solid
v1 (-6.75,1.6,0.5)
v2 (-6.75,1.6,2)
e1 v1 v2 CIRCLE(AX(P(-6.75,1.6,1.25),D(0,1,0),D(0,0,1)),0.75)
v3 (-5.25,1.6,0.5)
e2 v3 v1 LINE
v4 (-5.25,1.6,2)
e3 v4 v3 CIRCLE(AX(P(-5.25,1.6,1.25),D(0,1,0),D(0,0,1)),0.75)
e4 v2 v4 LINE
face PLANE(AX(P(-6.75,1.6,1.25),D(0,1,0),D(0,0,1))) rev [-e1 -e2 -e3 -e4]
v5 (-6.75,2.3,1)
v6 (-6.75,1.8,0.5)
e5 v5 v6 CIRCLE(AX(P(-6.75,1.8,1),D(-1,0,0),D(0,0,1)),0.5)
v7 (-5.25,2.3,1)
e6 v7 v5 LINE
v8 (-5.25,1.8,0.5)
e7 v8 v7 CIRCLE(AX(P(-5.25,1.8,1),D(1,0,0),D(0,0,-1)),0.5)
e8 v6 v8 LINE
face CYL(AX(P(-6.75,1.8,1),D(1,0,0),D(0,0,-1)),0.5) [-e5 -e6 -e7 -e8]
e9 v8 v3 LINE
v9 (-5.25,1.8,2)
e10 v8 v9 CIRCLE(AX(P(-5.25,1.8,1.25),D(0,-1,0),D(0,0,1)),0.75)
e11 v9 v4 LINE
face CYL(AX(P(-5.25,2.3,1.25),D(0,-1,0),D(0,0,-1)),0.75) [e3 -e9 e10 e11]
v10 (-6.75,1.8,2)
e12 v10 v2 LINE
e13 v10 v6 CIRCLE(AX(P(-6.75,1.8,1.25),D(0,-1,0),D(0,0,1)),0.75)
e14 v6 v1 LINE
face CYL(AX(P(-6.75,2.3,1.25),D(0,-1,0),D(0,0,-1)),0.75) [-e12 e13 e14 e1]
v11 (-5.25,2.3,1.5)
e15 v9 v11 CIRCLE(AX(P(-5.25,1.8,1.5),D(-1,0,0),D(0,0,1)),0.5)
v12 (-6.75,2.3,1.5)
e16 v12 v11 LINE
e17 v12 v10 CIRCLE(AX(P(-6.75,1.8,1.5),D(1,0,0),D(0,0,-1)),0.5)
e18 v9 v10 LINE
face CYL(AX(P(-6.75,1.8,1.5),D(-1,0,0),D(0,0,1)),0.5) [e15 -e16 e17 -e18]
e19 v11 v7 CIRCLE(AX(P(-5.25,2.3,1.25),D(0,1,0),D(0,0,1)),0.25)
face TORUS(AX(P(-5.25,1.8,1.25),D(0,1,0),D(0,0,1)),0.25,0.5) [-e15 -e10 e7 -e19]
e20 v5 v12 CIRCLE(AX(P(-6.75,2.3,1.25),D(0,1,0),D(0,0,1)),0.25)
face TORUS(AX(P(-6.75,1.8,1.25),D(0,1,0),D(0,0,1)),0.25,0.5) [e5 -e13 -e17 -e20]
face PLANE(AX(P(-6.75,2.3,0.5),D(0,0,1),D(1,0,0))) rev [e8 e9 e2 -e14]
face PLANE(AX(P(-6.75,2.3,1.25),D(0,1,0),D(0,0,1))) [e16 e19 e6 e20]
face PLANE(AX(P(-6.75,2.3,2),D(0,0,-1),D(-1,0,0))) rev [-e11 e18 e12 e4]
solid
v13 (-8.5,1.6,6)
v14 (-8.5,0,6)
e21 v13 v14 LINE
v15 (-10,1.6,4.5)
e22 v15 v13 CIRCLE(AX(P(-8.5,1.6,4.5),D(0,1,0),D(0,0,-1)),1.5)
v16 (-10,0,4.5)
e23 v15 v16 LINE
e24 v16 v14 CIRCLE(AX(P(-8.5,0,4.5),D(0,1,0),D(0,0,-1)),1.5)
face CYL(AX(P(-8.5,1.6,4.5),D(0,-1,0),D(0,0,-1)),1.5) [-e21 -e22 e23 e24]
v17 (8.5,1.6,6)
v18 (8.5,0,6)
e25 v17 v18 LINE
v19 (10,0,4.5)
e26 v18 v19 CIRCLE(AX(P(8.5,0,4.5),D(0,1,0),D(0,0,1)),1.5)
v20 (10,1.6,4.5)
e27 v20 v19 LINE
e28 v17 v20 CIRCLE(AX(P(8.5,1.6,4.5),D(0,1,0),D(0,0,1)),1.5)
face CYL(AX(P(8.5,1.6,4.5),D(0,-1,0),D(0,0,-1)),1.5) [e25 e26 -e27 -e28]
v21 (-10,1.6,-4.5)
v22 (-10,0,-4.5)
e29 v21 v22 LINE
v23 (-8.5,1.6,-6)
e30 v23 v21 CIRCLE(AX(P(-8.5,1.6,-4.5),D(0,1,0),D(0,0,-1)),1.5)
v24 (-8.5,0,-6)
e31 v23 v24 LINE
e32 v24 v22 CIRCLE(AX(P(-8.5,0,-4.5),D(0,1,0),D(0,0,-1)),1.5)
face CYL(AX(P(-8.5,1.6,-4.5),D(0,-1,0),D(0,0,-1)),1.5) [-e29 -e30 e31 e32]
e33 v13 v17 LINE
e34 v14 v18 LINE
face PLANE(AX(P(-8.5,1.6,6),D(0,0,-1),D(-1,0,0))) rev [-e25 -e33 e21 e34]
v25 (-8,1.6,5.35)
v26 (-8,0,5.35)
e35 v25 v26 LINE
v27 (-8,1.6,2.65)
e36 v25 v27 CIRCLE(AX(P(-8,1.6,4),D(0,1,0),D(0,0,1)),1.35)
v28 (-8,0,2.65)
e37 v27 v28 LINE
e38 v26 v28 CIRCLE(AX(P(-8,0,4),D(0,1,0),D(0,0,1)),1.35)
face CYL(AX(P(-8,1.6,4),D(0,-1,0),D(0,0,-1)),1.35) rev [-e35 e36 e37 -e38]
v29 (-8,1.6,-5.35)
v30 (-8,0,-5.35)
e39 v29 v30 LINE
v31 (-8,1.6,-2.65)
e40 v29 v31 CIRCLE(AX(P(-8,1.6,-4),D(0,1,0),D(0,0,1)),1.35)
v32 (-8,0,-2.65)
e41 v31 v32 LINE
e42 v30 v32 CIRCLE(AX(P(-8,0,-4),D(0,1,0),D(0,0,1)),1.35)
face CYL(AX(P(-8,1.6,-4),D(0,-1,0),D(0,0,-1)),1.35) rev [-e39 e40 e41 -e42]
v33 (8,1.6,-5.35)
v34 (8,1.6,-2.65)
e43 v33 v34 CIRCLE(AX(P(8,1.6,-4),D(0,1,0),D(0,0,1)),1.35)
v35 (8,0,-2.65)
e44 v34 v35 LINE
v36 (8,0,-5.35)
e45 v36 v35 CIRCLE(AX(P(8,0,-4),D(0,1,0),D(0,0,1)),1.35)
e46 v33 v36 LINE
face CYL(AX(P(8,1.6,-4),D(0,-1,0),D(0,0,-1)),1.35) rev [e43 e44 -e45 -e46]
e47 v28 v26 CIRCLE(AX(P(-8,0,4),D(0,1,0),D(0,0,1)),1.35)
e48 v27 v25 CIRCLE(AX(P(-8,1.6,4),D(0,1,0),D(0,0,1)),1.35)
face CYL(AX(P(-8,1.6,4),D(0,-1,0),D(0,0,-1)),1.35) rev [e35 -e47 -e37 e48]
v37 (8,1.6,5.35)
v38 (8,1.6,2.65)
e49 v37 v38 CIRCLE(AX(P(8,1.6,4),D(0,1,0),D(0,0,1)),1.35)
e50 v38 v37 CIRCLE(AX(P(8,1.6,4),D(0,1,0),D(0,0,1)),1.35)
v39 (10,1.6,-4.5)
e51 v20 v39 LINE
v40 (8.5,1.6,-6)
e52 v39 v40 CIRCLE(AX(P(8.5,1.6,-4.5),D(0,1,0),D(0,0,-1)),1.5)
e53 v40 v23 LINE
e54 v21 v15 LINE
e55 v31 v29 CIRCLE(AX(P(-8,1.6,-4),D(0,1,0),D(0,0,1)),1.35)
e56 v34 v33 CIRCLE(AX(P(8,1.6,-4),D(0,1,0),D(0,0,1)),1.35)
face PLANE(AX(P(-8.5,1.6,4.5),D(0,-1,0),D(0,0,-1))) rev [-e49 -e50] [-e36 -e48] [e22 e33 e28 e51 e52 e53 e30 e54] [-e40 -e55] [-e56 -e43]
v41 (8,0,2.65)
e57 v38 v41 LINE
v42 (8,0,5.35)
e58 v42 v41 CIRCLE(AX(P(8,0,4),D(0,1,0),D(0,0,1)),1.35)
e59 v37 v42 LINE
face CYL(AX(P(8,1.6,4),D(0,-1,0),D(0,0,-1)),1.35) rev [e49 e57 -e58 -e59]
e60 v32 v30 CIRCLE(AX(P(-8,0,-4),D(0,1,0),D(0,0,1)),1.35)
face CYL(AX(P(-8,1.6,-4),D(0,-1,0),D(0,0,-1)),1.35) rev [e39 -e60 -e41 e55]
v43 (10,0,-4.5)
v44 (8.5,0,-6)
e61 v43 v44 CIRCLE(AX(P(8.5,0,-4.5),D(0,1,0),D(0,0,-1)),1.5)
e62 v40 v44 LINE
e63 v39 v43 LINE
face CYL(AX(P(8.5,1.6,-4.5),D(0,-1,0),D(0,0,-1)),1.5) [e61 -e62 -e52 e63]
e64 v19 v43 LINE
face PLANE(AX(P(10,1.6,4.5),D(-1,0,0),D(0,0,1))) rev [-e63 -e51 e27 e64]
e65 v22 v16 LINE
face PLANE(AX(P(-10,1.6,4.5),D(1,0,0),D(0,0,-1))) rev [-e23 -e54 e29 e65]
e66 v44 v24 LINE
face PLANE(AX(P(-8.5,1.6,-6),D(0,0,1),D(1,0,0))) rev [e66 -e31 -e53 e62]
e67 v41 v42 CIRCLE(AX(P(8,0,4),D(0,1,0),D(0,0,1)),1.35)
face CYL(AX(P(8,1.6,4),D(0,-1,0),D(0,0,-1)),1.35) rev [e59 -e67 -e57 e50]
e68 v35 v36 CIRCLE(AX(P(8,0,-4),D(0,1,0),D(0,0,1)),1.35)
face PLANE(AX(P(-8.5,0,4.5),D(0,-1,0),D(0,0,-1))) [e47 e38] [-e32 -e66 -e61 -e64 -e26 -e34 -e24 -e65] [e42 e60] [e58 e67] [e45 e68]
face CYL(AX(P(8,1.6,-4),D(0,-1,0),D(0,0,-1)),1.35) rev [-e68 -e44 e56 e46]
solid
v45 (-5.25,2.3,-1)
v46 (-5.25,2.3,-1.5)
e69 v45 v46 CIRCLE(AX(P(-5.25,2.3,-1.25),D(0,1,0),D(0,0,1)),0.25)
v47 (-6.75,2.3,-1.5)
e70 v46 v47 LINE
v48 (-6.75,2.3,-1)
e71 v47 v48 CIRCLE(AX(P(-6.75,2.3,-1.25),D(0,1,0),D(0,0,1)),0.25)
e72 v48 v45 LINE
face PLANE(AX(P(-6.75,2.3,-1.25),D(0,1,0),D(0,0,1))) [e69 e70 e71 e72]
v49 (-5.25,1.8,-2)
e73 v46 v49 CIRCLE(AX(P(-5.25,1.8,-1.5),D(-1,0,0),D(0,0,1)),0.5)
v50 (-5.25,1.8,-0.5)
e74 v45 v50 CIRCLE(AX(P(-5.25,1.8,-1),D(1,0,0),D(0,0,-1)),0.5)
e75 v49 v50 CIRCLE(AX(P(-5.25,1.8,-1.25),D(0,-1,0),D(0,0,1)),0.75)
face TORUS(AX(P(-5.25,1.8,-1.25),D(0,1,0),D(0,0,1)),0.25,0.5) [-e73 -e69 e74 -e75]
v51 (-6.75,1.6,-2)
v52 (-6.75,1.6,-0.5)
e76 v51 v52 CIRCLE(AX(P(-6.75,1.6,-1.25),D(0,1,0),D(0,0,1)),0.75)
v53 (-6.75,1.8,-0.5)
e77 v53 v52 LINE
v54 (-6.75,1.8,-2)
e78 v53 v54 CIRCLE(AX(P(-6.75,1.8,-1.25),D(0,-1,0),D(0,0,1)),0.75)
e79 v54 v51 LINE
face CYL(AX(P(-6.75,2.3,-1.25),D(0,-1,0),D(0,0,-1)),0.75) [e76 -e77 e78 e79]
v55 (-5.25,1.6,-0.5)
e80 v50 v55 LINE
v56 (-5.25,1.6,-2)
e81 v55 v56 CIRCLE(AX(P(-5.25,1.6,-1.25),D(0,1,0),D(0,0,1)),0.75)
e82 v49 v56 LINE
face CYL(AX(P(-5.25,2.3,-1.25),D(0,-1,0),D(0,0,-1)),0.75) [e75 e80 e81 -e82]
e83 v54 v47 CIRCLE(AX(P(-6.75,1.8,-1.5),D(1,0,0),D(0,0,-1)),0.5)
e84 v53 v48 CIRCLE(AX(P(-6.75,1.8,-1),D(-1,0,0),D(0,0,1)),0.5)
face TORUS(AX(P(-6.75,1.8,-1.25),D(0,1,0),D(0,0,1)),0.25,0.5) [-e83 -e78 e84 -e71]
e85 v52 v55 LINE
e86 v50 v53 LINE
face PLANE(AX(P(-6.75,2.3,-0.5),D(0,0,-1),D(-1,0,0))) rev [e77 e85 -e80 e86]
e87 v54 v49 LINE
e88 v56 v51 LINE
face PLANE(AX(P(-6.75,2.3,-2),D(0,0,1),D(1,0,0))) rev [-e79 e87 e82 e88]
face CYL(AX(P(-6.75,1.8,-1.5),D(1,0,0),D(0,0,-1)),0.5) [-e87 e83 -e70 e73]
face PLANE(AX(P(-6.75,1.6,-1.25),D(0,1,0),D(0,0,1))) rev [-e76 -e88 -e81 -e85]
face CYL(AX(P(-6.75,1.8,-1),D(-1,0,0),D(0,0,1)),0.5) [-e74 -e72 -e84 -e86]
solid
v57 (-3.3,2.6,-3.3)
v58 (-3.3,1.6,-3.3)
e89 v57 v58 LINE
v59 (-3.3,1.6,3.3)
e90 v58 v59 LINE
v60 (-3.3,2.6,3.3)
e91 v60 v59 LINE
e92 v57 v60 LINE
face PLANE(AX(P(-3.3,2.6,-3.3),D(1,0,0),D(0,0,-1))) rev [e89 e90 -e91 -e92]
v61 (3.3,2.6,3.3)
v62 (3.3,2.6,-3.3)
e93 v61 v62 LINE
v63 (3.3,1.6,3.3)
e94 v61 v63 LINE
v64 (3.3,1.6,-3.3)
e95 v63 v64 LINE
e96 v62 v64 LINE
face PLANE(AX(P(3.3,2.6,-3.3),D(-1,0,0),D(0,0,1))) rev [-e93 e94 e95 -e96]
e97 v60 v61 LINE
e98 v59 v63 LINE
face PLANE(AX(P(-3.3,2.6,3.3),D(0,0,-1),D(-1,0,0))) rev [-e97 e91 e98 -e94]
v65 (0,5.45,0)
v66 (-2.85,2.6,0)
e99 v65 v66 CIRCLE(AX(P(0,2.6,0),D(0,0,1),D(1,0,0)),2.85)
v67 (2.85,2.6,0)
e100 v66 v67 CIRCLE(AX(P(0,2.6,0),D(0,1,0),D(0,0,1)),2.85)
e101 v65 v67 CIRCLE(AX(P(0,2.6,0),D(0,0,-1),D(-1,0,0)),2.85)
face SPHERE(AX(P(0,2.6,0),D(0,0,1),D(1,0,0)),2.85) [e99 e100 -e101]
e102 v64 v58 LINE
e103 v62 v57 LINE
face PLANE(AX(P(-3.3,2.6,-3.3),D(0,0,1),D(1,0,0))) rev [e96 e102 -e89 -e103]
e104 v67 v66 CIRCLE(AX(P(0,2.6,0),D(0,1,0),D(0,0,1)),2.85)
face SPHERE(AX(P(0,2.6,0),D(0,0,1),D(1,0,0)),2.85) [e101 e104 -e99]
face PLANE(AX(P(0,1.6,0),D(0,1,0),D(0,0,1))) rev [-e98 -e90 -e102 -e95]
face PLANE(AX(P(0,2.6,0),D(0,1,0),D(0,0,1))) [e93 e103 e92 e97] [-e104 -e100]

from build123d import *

# Parameters (mm, degrees)
ALUMINIUM_BASE_PLATE_DEPTH        = 1.6
SKETCH7_R                         = 1.35
SCREW_HOLE_DEPTH                  = 12.771151176
SKETCH_587_W                      = 6.6
SKETCH_587_H                      = 6.6
LED_BEAD_BOARD_DEPTH              = 1
SOLDER_JOINT_BASE_OUTLINE_DEPTH   = 0.7
SOLDER_JOINT_BASE_OUTLINE_2_DEPTH = 0.7
SOLDER_JOINT_1_R                  = 0.5
SOLDER_JOINT_2_R                  = 0.5


with BuildPart() as part:
    # Aluminium base plate outline → Aluminium base plate (new body)
    with BuildSketch(Plane(origin=(0, 0, 0), x_dir=(1, 0, 0), z_dir=(0, 1, 0))):
        with BuildLine():
            Line((-8.5, -6), (8.5, -6))
            ThreePointArc((8.5, -6), (9.560660172, -5.560660172), (10, -4.5))
            Line((10, -4.5), (10, 4.5))
            ThreePointArc((10, 4.5), (9.560660172, 5.560660172), (8.5, 6))
            Line((8.5, 6), (-8.5, 6))
            ThreePointArc((-8.5, 6), (-9.560660172, 5.560660172), (-10, 4.5))
            Line((-10, 4.5), (-10, -4.5))
            ThreePointArc((-10, -4.5), (-9.560660172, -5.560660172), (-8.5, -6))
        make_face()
    extrude(amount=ALUMINIUM_BASE_PLATE_DEPTH)

    # Sketch7 → Screw hole (cut, through all)
    with BuildSketch(Plane(origin=(0, 0, 0), x_dir=(1, 0, 0), z_dir=(0, 1, 0))):
        with Locations(Location((-8, -4, 0), (0, 0, 270))):
            Circle(SKETCH7_R)
        with Locations(Location((8, -4, 0), (0, 0, 270))):
            Circle(SKETCH7_R)
        with Locations(Location((8, 4, 0), (0, 0, 270))):
            Circle(SKETCH7_R)
        with Locations(Location((-8, 4, 0), (0, 0, 270))):
            Circle(SKETCH7_R)
    extrude(amount=SCREW_HOLE_DEPTH, mode=Mode.SUBTRACT)


with BuildPart() as body_2:
    # Sketch 587 → LED bead board (new body)
    with BuildSketch(Plane(origin=(0, 1.6, 0), x_dir=(1, 0, 0), z_dir=(0, 1, 0))):
        Rectangle(SKETCH_587_W, SKETCH_587_H)
    extrude(amount=LED_BEAD_BOARD_DEPTH)

    # LED bead rotation base → LED bead (revolve)
    with BuildSketch(Plane.XY):
        with BuildLine():
            Line((0, 2.6), (2.85, 2.6))
            ThreePointArc((2.85, 2.6), (2.015254326, 4.615254326), (0, 5.45))
            Line((0, 5.45), (0, 2.6))
        make_face()
    revolve(axis=Axis((0, 2.6, 0), (0, 1, 0)))


with BuildPart() as body_3:
    # Solder pad → Solder joint base outline (new body)
    with BuildSketch(Plane(origin=(0, 1.6, 0), x_dir=(1, 0, 0), z_dir=(0, 1, 0))):
        with BuildLine():
            Line((-6.75, 2), (-5.25, 2))
            ThreePointArc((-5.25, 2), (-4.5, 1.25), (-5.25, 0.5))
            Line((-5.25, 0.5), (-6.75, 0.5))
            ThreePointArc((-6.75, 0.5), (-7.5, 1.25), (-6.75, 2))
        make_face()
    extrude(amount=SOLDER_JOINT_BASE_OUTLINE_DEPTH)

    # Solder joint 1
    solder_joint_1_edges = [body_3.edges().sort_by_distance(p)[0] for p in [
        (-4.5, 2.3, -1.25),
        (-6, 2.3, -2),
        (-7.5, 2.3, -1.25),
        (-6, 2.3, -0.5),
    ]]
    fillet(solder_joint_1_edges, radius=SOLDER_JOINT_1_R)


with BuildPart() as body_4:
    # Solder pad → Solder joint base outline 2 (new body)
    with BuildSketch(Plane(origin=(0, 1.6, 0), x_dir=(1, 0, 0), z_dir=(0, 1, 0))):
        with BuildLine():
            Line((-6.75, -0.5), (-5.25, -0.5))
            ThreePointArc((-5.25, -0.5), (-4.5, -1.25), (-5.25, -2))
            Line((-5.25, -2), (-6.75, -2))
            ThreePointArc((-6.75, -2), (-7.5, -1.25), (-6.75, -0.5))
        make_face()
    extrude(amount=SOLDER_JOINT_BASE_OUTLINE_2_DEPTH)

    # Solder joint 2
    solder_joint_2_edges = [body_4.edges().sort_by_distance(p)[0] for p in [
        (-7.5, 2.3, 1.25),
        (-6, 2.3, 2),
        (-4.5, 2.3, 1.25),
        (-6, 2.3, 0.5),
    ]]
    fillet(solder_joint_2_edges, radius=SOLDER_JOINT_2_R)


solid = Compound([part.part, body_2.part, body_3.part, body_4.part])
